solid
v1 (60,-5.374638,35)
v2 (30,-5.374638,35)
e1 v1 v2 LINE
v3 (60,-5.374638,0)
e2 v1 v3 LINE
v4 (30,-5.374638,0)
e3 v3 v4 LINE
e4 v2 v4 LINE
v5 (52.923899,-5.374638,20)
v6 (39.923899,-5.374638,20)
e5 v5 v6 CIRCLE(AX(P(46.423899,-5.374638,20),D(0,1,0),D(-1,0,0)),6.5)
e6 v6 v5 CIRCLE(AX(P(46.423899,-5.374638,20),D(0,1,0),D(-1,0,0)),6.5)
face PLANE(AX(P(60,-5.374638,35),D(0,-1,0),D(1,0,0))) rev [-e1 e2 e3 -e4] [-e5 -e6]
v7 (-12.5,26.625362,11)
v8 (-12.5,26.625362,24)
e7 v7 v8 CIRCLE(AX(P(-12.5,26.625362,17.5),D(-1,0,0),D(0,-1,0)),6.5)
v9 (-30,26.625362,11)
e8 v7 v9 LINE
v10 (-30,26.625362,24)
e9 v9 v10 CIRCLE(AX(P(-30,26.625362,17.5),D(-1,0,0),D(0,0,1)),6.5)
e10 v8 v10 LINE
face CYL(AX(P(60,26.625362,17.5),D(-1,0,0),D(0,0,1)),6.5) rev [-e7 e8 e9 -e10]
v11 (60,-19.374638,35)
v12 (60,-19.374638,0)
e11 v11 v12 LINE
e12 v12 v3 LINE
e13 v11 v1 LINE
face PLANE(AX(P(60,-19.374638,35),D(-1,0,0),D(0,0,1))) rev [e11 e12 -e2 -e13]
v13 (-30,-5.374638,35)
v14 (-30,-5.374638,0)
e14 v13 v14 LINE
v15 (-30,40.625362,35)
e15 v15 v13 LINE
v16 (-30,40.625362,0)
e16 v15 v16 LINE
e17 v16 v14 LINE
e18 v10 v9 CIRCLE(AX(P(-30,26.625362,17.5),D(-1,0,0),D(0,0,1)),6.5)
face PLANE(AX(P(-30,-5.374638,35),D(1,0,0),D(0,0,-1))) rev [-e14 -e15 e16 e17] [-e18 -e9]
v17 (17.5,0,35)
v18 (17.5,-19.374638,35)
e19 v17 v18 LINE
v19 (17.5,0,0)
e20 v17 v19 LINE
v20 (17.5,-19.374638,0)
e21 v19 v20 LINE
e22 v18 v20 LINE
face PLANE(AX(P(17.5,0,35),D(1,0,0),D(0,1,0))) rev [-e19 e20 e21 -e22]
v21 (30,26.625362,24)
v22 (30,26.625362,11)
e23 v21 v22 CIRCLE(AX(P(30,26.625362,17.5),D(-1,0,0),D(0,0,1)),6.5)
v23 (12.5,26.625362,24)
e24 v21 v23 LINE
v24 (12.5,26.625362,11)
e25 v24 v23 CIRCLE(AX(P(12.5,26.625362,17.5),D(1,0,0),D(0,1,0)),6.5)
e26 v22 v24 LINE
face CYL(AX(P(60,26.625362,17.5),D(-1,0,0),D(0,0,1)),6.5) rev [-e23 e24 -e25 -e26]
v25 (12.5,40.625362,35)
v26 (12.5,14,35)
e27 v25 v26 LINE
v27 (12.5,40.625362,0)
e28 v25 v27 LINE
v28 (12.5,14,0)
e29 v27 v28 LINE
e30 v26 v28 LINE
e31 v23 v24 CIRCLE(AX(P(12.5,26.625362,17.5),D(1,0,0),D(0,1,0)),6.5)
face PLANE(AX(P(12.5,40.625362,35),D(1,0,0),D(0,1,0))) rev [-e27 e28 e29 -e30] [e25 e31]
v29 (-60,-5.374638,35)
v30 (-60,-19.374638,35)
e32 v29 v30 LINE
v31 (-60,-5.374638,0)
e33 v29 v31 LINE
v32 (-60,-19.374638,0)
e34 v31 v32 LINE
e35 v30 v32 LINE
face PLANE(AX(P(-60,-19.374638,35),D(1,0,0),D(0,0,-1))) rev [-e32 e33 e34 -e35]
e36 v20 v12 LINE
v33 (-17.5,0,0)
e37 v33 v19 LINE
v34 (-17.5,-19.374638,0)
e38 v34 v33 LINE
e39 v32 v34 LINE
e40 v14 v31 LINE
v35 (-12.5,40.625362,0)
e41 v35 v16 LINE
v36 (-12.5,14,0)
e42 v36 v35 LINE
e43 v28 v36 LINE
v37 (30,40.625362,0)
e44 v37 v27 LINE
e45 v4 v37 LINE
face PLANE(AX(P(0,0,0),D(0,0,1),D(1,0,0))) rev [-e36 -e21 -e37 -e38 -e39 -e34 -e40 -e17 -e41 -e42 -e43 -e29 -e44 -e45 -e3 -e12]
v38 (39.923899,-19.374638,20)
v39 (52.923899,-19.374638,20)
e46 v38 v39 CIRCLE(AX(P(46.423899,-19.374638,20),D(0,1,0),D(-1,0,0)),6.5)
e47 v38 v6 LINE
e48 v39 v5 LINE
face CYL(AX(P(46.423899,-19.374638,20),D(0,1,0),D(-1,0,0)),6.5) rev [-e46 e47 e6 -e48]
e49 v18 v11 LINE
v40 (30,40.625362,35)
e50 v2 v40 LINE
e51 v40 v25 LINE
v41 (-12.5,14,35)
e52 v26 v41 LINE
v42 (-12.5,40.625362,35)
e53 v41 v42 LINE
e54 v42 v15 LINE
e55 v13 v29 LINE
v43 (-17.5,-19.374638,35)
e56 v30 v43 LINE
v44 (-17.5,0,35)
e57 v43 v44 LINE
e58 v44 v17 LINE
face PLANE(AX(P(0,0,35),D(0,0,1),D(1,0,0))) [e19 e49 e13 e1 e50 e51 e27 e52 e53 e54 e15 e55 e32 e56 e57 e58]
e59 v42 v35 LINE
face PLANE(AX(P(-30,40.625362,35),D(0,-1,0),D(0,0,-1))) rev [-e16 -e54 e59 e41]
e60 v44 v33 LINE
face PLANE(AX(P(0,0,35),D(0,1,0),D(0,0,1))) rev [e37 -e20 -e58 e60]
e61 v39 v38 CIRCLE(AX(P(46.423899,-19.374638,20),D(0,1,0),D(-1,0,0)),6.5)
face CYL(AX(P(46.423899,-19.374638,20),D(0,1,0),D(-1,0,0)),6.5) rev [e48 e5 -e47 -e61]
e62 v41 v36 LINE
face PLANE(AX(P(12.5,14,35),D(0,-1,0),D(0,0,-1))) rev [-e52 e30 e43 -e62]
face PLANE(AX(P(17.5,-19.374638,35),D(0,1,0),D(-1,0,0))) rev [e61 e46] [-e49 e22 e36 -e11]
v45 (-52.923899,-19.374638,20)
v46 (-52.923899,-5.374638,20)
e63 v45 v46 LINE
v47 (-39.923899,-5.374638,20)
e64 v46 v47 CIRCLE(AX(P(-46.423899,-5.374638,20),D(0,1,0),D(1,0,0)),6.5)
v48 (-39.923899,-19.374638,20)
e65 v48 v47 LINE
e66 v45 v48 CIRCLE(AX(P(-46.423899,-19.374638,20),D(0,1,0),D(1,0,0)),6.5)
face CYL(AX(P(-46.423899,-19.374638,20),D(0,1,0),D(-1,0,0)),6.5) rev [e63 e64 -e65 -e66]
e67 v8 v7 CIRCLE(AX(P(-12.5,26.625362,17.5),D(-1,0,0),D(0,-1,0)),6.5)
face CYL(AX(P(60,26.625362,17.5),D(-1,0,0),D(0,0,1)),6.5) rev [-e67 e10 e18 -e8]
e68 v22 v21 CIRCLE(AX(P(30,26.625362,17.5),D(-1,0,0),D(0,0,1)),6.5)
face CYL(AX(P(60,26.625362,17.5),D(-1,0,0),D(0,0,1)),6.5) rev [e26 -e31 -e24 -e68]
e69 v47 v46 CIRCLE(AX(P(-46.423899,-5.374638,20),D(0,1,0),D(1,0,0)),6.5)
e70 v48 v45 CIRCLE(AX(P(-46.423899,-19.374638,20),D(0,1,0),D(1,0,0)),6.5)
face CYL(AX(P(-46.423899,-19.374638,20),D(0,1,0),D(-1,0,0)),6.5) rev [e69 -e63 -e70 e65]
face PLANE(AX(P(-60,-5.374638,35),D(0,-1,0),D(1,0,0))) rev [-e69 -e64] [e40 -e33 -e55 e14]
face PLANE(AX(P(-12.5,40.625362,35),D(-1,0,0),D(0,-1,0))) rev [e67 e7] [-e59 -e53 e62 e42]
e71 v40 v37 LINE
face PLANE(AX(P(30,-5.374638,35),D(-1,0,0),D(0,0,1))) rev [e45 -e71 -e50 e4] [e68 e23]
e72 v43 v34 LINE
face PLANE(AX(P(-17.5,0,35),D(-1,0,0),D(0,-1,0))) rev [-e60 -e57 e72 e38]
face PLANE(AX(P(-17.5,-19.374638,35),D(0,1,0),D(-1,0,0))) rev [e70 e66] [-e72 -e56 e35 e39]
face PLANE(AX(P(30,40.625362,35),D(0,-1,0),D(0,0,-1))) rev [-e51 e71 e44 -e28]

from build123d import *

# Parameters (mm, degrees)
FORK_BODY_DEPTH                 = 35
LUG_CROSS_HOLE_SKETCH_R         = 6.5
LUG_CROSS_HOLE_13_DEPTH         = 105.763638969
BASE_MOUNTING_HOLES_SKETCH_R    = 6.5
BASE_MOUNTING_HOLES_2X_13_DEPTH = 84.312664103


with BuildPart() as part:
    # Fork Profile Sketch → Fork Body (new body)
    with BuildSketch(Plane.XY):
        Polygon((0, 0), (17.5, 0), (17.5, -19.374637846), (60, -19.374637846), (60, -5.374637846), (30, -5.374637846), (30, 40.625362154), (12.5, 40.625362154), (12.5, 14), (-12.5, 14), (-12.5, 40.625362154), (-30, 40.625362154), (-30, -5.374637846), (-60, -5.374637846), (-60, -19.374637846), (-17.5, -19.374637846), (-17.5, 0), align=None)
    extrude(amount=FORK_BODY_DEPTH)

    # Lug Cross Hole Sketch → Lug Cross Hole Ø13 (cut, through all)
    with BuildSketch(Plane.ZY.offset(30)):
        with Locations((17.5, 26.625362154)):
            Circle(LUG_CROSS_HOLE_SKETCH_R)
    extrude(amount=-LUG_CROSS_HOLE_13_DEPTH, mode=Mode.SUBTRACT)

    # Base Mounting Holes Sketch → Base Mounting Holes 2xØ13 (cut, through all)
    with BuildSketch(Plane(origin=(0, -5.374637846, 0), x_dir=(1, 0, 0), z_dir=(0, 1, 0))):
        with Locations(Location((46.423898933, -20, 0), (0, 0, 180))):
            Circle(BASE_MOUNTING_HOLES_SKETCH_R)
        with Locations((-46.423898933, -20)):
            Circle(BASE_MOUNTING_HOLES_SKETCH_R)
    extrude(amount=-BASE_MOUNTING_HOLES_2X_13_DEPTH, mode=Mode.SUBTRACT)


solid = part.part
